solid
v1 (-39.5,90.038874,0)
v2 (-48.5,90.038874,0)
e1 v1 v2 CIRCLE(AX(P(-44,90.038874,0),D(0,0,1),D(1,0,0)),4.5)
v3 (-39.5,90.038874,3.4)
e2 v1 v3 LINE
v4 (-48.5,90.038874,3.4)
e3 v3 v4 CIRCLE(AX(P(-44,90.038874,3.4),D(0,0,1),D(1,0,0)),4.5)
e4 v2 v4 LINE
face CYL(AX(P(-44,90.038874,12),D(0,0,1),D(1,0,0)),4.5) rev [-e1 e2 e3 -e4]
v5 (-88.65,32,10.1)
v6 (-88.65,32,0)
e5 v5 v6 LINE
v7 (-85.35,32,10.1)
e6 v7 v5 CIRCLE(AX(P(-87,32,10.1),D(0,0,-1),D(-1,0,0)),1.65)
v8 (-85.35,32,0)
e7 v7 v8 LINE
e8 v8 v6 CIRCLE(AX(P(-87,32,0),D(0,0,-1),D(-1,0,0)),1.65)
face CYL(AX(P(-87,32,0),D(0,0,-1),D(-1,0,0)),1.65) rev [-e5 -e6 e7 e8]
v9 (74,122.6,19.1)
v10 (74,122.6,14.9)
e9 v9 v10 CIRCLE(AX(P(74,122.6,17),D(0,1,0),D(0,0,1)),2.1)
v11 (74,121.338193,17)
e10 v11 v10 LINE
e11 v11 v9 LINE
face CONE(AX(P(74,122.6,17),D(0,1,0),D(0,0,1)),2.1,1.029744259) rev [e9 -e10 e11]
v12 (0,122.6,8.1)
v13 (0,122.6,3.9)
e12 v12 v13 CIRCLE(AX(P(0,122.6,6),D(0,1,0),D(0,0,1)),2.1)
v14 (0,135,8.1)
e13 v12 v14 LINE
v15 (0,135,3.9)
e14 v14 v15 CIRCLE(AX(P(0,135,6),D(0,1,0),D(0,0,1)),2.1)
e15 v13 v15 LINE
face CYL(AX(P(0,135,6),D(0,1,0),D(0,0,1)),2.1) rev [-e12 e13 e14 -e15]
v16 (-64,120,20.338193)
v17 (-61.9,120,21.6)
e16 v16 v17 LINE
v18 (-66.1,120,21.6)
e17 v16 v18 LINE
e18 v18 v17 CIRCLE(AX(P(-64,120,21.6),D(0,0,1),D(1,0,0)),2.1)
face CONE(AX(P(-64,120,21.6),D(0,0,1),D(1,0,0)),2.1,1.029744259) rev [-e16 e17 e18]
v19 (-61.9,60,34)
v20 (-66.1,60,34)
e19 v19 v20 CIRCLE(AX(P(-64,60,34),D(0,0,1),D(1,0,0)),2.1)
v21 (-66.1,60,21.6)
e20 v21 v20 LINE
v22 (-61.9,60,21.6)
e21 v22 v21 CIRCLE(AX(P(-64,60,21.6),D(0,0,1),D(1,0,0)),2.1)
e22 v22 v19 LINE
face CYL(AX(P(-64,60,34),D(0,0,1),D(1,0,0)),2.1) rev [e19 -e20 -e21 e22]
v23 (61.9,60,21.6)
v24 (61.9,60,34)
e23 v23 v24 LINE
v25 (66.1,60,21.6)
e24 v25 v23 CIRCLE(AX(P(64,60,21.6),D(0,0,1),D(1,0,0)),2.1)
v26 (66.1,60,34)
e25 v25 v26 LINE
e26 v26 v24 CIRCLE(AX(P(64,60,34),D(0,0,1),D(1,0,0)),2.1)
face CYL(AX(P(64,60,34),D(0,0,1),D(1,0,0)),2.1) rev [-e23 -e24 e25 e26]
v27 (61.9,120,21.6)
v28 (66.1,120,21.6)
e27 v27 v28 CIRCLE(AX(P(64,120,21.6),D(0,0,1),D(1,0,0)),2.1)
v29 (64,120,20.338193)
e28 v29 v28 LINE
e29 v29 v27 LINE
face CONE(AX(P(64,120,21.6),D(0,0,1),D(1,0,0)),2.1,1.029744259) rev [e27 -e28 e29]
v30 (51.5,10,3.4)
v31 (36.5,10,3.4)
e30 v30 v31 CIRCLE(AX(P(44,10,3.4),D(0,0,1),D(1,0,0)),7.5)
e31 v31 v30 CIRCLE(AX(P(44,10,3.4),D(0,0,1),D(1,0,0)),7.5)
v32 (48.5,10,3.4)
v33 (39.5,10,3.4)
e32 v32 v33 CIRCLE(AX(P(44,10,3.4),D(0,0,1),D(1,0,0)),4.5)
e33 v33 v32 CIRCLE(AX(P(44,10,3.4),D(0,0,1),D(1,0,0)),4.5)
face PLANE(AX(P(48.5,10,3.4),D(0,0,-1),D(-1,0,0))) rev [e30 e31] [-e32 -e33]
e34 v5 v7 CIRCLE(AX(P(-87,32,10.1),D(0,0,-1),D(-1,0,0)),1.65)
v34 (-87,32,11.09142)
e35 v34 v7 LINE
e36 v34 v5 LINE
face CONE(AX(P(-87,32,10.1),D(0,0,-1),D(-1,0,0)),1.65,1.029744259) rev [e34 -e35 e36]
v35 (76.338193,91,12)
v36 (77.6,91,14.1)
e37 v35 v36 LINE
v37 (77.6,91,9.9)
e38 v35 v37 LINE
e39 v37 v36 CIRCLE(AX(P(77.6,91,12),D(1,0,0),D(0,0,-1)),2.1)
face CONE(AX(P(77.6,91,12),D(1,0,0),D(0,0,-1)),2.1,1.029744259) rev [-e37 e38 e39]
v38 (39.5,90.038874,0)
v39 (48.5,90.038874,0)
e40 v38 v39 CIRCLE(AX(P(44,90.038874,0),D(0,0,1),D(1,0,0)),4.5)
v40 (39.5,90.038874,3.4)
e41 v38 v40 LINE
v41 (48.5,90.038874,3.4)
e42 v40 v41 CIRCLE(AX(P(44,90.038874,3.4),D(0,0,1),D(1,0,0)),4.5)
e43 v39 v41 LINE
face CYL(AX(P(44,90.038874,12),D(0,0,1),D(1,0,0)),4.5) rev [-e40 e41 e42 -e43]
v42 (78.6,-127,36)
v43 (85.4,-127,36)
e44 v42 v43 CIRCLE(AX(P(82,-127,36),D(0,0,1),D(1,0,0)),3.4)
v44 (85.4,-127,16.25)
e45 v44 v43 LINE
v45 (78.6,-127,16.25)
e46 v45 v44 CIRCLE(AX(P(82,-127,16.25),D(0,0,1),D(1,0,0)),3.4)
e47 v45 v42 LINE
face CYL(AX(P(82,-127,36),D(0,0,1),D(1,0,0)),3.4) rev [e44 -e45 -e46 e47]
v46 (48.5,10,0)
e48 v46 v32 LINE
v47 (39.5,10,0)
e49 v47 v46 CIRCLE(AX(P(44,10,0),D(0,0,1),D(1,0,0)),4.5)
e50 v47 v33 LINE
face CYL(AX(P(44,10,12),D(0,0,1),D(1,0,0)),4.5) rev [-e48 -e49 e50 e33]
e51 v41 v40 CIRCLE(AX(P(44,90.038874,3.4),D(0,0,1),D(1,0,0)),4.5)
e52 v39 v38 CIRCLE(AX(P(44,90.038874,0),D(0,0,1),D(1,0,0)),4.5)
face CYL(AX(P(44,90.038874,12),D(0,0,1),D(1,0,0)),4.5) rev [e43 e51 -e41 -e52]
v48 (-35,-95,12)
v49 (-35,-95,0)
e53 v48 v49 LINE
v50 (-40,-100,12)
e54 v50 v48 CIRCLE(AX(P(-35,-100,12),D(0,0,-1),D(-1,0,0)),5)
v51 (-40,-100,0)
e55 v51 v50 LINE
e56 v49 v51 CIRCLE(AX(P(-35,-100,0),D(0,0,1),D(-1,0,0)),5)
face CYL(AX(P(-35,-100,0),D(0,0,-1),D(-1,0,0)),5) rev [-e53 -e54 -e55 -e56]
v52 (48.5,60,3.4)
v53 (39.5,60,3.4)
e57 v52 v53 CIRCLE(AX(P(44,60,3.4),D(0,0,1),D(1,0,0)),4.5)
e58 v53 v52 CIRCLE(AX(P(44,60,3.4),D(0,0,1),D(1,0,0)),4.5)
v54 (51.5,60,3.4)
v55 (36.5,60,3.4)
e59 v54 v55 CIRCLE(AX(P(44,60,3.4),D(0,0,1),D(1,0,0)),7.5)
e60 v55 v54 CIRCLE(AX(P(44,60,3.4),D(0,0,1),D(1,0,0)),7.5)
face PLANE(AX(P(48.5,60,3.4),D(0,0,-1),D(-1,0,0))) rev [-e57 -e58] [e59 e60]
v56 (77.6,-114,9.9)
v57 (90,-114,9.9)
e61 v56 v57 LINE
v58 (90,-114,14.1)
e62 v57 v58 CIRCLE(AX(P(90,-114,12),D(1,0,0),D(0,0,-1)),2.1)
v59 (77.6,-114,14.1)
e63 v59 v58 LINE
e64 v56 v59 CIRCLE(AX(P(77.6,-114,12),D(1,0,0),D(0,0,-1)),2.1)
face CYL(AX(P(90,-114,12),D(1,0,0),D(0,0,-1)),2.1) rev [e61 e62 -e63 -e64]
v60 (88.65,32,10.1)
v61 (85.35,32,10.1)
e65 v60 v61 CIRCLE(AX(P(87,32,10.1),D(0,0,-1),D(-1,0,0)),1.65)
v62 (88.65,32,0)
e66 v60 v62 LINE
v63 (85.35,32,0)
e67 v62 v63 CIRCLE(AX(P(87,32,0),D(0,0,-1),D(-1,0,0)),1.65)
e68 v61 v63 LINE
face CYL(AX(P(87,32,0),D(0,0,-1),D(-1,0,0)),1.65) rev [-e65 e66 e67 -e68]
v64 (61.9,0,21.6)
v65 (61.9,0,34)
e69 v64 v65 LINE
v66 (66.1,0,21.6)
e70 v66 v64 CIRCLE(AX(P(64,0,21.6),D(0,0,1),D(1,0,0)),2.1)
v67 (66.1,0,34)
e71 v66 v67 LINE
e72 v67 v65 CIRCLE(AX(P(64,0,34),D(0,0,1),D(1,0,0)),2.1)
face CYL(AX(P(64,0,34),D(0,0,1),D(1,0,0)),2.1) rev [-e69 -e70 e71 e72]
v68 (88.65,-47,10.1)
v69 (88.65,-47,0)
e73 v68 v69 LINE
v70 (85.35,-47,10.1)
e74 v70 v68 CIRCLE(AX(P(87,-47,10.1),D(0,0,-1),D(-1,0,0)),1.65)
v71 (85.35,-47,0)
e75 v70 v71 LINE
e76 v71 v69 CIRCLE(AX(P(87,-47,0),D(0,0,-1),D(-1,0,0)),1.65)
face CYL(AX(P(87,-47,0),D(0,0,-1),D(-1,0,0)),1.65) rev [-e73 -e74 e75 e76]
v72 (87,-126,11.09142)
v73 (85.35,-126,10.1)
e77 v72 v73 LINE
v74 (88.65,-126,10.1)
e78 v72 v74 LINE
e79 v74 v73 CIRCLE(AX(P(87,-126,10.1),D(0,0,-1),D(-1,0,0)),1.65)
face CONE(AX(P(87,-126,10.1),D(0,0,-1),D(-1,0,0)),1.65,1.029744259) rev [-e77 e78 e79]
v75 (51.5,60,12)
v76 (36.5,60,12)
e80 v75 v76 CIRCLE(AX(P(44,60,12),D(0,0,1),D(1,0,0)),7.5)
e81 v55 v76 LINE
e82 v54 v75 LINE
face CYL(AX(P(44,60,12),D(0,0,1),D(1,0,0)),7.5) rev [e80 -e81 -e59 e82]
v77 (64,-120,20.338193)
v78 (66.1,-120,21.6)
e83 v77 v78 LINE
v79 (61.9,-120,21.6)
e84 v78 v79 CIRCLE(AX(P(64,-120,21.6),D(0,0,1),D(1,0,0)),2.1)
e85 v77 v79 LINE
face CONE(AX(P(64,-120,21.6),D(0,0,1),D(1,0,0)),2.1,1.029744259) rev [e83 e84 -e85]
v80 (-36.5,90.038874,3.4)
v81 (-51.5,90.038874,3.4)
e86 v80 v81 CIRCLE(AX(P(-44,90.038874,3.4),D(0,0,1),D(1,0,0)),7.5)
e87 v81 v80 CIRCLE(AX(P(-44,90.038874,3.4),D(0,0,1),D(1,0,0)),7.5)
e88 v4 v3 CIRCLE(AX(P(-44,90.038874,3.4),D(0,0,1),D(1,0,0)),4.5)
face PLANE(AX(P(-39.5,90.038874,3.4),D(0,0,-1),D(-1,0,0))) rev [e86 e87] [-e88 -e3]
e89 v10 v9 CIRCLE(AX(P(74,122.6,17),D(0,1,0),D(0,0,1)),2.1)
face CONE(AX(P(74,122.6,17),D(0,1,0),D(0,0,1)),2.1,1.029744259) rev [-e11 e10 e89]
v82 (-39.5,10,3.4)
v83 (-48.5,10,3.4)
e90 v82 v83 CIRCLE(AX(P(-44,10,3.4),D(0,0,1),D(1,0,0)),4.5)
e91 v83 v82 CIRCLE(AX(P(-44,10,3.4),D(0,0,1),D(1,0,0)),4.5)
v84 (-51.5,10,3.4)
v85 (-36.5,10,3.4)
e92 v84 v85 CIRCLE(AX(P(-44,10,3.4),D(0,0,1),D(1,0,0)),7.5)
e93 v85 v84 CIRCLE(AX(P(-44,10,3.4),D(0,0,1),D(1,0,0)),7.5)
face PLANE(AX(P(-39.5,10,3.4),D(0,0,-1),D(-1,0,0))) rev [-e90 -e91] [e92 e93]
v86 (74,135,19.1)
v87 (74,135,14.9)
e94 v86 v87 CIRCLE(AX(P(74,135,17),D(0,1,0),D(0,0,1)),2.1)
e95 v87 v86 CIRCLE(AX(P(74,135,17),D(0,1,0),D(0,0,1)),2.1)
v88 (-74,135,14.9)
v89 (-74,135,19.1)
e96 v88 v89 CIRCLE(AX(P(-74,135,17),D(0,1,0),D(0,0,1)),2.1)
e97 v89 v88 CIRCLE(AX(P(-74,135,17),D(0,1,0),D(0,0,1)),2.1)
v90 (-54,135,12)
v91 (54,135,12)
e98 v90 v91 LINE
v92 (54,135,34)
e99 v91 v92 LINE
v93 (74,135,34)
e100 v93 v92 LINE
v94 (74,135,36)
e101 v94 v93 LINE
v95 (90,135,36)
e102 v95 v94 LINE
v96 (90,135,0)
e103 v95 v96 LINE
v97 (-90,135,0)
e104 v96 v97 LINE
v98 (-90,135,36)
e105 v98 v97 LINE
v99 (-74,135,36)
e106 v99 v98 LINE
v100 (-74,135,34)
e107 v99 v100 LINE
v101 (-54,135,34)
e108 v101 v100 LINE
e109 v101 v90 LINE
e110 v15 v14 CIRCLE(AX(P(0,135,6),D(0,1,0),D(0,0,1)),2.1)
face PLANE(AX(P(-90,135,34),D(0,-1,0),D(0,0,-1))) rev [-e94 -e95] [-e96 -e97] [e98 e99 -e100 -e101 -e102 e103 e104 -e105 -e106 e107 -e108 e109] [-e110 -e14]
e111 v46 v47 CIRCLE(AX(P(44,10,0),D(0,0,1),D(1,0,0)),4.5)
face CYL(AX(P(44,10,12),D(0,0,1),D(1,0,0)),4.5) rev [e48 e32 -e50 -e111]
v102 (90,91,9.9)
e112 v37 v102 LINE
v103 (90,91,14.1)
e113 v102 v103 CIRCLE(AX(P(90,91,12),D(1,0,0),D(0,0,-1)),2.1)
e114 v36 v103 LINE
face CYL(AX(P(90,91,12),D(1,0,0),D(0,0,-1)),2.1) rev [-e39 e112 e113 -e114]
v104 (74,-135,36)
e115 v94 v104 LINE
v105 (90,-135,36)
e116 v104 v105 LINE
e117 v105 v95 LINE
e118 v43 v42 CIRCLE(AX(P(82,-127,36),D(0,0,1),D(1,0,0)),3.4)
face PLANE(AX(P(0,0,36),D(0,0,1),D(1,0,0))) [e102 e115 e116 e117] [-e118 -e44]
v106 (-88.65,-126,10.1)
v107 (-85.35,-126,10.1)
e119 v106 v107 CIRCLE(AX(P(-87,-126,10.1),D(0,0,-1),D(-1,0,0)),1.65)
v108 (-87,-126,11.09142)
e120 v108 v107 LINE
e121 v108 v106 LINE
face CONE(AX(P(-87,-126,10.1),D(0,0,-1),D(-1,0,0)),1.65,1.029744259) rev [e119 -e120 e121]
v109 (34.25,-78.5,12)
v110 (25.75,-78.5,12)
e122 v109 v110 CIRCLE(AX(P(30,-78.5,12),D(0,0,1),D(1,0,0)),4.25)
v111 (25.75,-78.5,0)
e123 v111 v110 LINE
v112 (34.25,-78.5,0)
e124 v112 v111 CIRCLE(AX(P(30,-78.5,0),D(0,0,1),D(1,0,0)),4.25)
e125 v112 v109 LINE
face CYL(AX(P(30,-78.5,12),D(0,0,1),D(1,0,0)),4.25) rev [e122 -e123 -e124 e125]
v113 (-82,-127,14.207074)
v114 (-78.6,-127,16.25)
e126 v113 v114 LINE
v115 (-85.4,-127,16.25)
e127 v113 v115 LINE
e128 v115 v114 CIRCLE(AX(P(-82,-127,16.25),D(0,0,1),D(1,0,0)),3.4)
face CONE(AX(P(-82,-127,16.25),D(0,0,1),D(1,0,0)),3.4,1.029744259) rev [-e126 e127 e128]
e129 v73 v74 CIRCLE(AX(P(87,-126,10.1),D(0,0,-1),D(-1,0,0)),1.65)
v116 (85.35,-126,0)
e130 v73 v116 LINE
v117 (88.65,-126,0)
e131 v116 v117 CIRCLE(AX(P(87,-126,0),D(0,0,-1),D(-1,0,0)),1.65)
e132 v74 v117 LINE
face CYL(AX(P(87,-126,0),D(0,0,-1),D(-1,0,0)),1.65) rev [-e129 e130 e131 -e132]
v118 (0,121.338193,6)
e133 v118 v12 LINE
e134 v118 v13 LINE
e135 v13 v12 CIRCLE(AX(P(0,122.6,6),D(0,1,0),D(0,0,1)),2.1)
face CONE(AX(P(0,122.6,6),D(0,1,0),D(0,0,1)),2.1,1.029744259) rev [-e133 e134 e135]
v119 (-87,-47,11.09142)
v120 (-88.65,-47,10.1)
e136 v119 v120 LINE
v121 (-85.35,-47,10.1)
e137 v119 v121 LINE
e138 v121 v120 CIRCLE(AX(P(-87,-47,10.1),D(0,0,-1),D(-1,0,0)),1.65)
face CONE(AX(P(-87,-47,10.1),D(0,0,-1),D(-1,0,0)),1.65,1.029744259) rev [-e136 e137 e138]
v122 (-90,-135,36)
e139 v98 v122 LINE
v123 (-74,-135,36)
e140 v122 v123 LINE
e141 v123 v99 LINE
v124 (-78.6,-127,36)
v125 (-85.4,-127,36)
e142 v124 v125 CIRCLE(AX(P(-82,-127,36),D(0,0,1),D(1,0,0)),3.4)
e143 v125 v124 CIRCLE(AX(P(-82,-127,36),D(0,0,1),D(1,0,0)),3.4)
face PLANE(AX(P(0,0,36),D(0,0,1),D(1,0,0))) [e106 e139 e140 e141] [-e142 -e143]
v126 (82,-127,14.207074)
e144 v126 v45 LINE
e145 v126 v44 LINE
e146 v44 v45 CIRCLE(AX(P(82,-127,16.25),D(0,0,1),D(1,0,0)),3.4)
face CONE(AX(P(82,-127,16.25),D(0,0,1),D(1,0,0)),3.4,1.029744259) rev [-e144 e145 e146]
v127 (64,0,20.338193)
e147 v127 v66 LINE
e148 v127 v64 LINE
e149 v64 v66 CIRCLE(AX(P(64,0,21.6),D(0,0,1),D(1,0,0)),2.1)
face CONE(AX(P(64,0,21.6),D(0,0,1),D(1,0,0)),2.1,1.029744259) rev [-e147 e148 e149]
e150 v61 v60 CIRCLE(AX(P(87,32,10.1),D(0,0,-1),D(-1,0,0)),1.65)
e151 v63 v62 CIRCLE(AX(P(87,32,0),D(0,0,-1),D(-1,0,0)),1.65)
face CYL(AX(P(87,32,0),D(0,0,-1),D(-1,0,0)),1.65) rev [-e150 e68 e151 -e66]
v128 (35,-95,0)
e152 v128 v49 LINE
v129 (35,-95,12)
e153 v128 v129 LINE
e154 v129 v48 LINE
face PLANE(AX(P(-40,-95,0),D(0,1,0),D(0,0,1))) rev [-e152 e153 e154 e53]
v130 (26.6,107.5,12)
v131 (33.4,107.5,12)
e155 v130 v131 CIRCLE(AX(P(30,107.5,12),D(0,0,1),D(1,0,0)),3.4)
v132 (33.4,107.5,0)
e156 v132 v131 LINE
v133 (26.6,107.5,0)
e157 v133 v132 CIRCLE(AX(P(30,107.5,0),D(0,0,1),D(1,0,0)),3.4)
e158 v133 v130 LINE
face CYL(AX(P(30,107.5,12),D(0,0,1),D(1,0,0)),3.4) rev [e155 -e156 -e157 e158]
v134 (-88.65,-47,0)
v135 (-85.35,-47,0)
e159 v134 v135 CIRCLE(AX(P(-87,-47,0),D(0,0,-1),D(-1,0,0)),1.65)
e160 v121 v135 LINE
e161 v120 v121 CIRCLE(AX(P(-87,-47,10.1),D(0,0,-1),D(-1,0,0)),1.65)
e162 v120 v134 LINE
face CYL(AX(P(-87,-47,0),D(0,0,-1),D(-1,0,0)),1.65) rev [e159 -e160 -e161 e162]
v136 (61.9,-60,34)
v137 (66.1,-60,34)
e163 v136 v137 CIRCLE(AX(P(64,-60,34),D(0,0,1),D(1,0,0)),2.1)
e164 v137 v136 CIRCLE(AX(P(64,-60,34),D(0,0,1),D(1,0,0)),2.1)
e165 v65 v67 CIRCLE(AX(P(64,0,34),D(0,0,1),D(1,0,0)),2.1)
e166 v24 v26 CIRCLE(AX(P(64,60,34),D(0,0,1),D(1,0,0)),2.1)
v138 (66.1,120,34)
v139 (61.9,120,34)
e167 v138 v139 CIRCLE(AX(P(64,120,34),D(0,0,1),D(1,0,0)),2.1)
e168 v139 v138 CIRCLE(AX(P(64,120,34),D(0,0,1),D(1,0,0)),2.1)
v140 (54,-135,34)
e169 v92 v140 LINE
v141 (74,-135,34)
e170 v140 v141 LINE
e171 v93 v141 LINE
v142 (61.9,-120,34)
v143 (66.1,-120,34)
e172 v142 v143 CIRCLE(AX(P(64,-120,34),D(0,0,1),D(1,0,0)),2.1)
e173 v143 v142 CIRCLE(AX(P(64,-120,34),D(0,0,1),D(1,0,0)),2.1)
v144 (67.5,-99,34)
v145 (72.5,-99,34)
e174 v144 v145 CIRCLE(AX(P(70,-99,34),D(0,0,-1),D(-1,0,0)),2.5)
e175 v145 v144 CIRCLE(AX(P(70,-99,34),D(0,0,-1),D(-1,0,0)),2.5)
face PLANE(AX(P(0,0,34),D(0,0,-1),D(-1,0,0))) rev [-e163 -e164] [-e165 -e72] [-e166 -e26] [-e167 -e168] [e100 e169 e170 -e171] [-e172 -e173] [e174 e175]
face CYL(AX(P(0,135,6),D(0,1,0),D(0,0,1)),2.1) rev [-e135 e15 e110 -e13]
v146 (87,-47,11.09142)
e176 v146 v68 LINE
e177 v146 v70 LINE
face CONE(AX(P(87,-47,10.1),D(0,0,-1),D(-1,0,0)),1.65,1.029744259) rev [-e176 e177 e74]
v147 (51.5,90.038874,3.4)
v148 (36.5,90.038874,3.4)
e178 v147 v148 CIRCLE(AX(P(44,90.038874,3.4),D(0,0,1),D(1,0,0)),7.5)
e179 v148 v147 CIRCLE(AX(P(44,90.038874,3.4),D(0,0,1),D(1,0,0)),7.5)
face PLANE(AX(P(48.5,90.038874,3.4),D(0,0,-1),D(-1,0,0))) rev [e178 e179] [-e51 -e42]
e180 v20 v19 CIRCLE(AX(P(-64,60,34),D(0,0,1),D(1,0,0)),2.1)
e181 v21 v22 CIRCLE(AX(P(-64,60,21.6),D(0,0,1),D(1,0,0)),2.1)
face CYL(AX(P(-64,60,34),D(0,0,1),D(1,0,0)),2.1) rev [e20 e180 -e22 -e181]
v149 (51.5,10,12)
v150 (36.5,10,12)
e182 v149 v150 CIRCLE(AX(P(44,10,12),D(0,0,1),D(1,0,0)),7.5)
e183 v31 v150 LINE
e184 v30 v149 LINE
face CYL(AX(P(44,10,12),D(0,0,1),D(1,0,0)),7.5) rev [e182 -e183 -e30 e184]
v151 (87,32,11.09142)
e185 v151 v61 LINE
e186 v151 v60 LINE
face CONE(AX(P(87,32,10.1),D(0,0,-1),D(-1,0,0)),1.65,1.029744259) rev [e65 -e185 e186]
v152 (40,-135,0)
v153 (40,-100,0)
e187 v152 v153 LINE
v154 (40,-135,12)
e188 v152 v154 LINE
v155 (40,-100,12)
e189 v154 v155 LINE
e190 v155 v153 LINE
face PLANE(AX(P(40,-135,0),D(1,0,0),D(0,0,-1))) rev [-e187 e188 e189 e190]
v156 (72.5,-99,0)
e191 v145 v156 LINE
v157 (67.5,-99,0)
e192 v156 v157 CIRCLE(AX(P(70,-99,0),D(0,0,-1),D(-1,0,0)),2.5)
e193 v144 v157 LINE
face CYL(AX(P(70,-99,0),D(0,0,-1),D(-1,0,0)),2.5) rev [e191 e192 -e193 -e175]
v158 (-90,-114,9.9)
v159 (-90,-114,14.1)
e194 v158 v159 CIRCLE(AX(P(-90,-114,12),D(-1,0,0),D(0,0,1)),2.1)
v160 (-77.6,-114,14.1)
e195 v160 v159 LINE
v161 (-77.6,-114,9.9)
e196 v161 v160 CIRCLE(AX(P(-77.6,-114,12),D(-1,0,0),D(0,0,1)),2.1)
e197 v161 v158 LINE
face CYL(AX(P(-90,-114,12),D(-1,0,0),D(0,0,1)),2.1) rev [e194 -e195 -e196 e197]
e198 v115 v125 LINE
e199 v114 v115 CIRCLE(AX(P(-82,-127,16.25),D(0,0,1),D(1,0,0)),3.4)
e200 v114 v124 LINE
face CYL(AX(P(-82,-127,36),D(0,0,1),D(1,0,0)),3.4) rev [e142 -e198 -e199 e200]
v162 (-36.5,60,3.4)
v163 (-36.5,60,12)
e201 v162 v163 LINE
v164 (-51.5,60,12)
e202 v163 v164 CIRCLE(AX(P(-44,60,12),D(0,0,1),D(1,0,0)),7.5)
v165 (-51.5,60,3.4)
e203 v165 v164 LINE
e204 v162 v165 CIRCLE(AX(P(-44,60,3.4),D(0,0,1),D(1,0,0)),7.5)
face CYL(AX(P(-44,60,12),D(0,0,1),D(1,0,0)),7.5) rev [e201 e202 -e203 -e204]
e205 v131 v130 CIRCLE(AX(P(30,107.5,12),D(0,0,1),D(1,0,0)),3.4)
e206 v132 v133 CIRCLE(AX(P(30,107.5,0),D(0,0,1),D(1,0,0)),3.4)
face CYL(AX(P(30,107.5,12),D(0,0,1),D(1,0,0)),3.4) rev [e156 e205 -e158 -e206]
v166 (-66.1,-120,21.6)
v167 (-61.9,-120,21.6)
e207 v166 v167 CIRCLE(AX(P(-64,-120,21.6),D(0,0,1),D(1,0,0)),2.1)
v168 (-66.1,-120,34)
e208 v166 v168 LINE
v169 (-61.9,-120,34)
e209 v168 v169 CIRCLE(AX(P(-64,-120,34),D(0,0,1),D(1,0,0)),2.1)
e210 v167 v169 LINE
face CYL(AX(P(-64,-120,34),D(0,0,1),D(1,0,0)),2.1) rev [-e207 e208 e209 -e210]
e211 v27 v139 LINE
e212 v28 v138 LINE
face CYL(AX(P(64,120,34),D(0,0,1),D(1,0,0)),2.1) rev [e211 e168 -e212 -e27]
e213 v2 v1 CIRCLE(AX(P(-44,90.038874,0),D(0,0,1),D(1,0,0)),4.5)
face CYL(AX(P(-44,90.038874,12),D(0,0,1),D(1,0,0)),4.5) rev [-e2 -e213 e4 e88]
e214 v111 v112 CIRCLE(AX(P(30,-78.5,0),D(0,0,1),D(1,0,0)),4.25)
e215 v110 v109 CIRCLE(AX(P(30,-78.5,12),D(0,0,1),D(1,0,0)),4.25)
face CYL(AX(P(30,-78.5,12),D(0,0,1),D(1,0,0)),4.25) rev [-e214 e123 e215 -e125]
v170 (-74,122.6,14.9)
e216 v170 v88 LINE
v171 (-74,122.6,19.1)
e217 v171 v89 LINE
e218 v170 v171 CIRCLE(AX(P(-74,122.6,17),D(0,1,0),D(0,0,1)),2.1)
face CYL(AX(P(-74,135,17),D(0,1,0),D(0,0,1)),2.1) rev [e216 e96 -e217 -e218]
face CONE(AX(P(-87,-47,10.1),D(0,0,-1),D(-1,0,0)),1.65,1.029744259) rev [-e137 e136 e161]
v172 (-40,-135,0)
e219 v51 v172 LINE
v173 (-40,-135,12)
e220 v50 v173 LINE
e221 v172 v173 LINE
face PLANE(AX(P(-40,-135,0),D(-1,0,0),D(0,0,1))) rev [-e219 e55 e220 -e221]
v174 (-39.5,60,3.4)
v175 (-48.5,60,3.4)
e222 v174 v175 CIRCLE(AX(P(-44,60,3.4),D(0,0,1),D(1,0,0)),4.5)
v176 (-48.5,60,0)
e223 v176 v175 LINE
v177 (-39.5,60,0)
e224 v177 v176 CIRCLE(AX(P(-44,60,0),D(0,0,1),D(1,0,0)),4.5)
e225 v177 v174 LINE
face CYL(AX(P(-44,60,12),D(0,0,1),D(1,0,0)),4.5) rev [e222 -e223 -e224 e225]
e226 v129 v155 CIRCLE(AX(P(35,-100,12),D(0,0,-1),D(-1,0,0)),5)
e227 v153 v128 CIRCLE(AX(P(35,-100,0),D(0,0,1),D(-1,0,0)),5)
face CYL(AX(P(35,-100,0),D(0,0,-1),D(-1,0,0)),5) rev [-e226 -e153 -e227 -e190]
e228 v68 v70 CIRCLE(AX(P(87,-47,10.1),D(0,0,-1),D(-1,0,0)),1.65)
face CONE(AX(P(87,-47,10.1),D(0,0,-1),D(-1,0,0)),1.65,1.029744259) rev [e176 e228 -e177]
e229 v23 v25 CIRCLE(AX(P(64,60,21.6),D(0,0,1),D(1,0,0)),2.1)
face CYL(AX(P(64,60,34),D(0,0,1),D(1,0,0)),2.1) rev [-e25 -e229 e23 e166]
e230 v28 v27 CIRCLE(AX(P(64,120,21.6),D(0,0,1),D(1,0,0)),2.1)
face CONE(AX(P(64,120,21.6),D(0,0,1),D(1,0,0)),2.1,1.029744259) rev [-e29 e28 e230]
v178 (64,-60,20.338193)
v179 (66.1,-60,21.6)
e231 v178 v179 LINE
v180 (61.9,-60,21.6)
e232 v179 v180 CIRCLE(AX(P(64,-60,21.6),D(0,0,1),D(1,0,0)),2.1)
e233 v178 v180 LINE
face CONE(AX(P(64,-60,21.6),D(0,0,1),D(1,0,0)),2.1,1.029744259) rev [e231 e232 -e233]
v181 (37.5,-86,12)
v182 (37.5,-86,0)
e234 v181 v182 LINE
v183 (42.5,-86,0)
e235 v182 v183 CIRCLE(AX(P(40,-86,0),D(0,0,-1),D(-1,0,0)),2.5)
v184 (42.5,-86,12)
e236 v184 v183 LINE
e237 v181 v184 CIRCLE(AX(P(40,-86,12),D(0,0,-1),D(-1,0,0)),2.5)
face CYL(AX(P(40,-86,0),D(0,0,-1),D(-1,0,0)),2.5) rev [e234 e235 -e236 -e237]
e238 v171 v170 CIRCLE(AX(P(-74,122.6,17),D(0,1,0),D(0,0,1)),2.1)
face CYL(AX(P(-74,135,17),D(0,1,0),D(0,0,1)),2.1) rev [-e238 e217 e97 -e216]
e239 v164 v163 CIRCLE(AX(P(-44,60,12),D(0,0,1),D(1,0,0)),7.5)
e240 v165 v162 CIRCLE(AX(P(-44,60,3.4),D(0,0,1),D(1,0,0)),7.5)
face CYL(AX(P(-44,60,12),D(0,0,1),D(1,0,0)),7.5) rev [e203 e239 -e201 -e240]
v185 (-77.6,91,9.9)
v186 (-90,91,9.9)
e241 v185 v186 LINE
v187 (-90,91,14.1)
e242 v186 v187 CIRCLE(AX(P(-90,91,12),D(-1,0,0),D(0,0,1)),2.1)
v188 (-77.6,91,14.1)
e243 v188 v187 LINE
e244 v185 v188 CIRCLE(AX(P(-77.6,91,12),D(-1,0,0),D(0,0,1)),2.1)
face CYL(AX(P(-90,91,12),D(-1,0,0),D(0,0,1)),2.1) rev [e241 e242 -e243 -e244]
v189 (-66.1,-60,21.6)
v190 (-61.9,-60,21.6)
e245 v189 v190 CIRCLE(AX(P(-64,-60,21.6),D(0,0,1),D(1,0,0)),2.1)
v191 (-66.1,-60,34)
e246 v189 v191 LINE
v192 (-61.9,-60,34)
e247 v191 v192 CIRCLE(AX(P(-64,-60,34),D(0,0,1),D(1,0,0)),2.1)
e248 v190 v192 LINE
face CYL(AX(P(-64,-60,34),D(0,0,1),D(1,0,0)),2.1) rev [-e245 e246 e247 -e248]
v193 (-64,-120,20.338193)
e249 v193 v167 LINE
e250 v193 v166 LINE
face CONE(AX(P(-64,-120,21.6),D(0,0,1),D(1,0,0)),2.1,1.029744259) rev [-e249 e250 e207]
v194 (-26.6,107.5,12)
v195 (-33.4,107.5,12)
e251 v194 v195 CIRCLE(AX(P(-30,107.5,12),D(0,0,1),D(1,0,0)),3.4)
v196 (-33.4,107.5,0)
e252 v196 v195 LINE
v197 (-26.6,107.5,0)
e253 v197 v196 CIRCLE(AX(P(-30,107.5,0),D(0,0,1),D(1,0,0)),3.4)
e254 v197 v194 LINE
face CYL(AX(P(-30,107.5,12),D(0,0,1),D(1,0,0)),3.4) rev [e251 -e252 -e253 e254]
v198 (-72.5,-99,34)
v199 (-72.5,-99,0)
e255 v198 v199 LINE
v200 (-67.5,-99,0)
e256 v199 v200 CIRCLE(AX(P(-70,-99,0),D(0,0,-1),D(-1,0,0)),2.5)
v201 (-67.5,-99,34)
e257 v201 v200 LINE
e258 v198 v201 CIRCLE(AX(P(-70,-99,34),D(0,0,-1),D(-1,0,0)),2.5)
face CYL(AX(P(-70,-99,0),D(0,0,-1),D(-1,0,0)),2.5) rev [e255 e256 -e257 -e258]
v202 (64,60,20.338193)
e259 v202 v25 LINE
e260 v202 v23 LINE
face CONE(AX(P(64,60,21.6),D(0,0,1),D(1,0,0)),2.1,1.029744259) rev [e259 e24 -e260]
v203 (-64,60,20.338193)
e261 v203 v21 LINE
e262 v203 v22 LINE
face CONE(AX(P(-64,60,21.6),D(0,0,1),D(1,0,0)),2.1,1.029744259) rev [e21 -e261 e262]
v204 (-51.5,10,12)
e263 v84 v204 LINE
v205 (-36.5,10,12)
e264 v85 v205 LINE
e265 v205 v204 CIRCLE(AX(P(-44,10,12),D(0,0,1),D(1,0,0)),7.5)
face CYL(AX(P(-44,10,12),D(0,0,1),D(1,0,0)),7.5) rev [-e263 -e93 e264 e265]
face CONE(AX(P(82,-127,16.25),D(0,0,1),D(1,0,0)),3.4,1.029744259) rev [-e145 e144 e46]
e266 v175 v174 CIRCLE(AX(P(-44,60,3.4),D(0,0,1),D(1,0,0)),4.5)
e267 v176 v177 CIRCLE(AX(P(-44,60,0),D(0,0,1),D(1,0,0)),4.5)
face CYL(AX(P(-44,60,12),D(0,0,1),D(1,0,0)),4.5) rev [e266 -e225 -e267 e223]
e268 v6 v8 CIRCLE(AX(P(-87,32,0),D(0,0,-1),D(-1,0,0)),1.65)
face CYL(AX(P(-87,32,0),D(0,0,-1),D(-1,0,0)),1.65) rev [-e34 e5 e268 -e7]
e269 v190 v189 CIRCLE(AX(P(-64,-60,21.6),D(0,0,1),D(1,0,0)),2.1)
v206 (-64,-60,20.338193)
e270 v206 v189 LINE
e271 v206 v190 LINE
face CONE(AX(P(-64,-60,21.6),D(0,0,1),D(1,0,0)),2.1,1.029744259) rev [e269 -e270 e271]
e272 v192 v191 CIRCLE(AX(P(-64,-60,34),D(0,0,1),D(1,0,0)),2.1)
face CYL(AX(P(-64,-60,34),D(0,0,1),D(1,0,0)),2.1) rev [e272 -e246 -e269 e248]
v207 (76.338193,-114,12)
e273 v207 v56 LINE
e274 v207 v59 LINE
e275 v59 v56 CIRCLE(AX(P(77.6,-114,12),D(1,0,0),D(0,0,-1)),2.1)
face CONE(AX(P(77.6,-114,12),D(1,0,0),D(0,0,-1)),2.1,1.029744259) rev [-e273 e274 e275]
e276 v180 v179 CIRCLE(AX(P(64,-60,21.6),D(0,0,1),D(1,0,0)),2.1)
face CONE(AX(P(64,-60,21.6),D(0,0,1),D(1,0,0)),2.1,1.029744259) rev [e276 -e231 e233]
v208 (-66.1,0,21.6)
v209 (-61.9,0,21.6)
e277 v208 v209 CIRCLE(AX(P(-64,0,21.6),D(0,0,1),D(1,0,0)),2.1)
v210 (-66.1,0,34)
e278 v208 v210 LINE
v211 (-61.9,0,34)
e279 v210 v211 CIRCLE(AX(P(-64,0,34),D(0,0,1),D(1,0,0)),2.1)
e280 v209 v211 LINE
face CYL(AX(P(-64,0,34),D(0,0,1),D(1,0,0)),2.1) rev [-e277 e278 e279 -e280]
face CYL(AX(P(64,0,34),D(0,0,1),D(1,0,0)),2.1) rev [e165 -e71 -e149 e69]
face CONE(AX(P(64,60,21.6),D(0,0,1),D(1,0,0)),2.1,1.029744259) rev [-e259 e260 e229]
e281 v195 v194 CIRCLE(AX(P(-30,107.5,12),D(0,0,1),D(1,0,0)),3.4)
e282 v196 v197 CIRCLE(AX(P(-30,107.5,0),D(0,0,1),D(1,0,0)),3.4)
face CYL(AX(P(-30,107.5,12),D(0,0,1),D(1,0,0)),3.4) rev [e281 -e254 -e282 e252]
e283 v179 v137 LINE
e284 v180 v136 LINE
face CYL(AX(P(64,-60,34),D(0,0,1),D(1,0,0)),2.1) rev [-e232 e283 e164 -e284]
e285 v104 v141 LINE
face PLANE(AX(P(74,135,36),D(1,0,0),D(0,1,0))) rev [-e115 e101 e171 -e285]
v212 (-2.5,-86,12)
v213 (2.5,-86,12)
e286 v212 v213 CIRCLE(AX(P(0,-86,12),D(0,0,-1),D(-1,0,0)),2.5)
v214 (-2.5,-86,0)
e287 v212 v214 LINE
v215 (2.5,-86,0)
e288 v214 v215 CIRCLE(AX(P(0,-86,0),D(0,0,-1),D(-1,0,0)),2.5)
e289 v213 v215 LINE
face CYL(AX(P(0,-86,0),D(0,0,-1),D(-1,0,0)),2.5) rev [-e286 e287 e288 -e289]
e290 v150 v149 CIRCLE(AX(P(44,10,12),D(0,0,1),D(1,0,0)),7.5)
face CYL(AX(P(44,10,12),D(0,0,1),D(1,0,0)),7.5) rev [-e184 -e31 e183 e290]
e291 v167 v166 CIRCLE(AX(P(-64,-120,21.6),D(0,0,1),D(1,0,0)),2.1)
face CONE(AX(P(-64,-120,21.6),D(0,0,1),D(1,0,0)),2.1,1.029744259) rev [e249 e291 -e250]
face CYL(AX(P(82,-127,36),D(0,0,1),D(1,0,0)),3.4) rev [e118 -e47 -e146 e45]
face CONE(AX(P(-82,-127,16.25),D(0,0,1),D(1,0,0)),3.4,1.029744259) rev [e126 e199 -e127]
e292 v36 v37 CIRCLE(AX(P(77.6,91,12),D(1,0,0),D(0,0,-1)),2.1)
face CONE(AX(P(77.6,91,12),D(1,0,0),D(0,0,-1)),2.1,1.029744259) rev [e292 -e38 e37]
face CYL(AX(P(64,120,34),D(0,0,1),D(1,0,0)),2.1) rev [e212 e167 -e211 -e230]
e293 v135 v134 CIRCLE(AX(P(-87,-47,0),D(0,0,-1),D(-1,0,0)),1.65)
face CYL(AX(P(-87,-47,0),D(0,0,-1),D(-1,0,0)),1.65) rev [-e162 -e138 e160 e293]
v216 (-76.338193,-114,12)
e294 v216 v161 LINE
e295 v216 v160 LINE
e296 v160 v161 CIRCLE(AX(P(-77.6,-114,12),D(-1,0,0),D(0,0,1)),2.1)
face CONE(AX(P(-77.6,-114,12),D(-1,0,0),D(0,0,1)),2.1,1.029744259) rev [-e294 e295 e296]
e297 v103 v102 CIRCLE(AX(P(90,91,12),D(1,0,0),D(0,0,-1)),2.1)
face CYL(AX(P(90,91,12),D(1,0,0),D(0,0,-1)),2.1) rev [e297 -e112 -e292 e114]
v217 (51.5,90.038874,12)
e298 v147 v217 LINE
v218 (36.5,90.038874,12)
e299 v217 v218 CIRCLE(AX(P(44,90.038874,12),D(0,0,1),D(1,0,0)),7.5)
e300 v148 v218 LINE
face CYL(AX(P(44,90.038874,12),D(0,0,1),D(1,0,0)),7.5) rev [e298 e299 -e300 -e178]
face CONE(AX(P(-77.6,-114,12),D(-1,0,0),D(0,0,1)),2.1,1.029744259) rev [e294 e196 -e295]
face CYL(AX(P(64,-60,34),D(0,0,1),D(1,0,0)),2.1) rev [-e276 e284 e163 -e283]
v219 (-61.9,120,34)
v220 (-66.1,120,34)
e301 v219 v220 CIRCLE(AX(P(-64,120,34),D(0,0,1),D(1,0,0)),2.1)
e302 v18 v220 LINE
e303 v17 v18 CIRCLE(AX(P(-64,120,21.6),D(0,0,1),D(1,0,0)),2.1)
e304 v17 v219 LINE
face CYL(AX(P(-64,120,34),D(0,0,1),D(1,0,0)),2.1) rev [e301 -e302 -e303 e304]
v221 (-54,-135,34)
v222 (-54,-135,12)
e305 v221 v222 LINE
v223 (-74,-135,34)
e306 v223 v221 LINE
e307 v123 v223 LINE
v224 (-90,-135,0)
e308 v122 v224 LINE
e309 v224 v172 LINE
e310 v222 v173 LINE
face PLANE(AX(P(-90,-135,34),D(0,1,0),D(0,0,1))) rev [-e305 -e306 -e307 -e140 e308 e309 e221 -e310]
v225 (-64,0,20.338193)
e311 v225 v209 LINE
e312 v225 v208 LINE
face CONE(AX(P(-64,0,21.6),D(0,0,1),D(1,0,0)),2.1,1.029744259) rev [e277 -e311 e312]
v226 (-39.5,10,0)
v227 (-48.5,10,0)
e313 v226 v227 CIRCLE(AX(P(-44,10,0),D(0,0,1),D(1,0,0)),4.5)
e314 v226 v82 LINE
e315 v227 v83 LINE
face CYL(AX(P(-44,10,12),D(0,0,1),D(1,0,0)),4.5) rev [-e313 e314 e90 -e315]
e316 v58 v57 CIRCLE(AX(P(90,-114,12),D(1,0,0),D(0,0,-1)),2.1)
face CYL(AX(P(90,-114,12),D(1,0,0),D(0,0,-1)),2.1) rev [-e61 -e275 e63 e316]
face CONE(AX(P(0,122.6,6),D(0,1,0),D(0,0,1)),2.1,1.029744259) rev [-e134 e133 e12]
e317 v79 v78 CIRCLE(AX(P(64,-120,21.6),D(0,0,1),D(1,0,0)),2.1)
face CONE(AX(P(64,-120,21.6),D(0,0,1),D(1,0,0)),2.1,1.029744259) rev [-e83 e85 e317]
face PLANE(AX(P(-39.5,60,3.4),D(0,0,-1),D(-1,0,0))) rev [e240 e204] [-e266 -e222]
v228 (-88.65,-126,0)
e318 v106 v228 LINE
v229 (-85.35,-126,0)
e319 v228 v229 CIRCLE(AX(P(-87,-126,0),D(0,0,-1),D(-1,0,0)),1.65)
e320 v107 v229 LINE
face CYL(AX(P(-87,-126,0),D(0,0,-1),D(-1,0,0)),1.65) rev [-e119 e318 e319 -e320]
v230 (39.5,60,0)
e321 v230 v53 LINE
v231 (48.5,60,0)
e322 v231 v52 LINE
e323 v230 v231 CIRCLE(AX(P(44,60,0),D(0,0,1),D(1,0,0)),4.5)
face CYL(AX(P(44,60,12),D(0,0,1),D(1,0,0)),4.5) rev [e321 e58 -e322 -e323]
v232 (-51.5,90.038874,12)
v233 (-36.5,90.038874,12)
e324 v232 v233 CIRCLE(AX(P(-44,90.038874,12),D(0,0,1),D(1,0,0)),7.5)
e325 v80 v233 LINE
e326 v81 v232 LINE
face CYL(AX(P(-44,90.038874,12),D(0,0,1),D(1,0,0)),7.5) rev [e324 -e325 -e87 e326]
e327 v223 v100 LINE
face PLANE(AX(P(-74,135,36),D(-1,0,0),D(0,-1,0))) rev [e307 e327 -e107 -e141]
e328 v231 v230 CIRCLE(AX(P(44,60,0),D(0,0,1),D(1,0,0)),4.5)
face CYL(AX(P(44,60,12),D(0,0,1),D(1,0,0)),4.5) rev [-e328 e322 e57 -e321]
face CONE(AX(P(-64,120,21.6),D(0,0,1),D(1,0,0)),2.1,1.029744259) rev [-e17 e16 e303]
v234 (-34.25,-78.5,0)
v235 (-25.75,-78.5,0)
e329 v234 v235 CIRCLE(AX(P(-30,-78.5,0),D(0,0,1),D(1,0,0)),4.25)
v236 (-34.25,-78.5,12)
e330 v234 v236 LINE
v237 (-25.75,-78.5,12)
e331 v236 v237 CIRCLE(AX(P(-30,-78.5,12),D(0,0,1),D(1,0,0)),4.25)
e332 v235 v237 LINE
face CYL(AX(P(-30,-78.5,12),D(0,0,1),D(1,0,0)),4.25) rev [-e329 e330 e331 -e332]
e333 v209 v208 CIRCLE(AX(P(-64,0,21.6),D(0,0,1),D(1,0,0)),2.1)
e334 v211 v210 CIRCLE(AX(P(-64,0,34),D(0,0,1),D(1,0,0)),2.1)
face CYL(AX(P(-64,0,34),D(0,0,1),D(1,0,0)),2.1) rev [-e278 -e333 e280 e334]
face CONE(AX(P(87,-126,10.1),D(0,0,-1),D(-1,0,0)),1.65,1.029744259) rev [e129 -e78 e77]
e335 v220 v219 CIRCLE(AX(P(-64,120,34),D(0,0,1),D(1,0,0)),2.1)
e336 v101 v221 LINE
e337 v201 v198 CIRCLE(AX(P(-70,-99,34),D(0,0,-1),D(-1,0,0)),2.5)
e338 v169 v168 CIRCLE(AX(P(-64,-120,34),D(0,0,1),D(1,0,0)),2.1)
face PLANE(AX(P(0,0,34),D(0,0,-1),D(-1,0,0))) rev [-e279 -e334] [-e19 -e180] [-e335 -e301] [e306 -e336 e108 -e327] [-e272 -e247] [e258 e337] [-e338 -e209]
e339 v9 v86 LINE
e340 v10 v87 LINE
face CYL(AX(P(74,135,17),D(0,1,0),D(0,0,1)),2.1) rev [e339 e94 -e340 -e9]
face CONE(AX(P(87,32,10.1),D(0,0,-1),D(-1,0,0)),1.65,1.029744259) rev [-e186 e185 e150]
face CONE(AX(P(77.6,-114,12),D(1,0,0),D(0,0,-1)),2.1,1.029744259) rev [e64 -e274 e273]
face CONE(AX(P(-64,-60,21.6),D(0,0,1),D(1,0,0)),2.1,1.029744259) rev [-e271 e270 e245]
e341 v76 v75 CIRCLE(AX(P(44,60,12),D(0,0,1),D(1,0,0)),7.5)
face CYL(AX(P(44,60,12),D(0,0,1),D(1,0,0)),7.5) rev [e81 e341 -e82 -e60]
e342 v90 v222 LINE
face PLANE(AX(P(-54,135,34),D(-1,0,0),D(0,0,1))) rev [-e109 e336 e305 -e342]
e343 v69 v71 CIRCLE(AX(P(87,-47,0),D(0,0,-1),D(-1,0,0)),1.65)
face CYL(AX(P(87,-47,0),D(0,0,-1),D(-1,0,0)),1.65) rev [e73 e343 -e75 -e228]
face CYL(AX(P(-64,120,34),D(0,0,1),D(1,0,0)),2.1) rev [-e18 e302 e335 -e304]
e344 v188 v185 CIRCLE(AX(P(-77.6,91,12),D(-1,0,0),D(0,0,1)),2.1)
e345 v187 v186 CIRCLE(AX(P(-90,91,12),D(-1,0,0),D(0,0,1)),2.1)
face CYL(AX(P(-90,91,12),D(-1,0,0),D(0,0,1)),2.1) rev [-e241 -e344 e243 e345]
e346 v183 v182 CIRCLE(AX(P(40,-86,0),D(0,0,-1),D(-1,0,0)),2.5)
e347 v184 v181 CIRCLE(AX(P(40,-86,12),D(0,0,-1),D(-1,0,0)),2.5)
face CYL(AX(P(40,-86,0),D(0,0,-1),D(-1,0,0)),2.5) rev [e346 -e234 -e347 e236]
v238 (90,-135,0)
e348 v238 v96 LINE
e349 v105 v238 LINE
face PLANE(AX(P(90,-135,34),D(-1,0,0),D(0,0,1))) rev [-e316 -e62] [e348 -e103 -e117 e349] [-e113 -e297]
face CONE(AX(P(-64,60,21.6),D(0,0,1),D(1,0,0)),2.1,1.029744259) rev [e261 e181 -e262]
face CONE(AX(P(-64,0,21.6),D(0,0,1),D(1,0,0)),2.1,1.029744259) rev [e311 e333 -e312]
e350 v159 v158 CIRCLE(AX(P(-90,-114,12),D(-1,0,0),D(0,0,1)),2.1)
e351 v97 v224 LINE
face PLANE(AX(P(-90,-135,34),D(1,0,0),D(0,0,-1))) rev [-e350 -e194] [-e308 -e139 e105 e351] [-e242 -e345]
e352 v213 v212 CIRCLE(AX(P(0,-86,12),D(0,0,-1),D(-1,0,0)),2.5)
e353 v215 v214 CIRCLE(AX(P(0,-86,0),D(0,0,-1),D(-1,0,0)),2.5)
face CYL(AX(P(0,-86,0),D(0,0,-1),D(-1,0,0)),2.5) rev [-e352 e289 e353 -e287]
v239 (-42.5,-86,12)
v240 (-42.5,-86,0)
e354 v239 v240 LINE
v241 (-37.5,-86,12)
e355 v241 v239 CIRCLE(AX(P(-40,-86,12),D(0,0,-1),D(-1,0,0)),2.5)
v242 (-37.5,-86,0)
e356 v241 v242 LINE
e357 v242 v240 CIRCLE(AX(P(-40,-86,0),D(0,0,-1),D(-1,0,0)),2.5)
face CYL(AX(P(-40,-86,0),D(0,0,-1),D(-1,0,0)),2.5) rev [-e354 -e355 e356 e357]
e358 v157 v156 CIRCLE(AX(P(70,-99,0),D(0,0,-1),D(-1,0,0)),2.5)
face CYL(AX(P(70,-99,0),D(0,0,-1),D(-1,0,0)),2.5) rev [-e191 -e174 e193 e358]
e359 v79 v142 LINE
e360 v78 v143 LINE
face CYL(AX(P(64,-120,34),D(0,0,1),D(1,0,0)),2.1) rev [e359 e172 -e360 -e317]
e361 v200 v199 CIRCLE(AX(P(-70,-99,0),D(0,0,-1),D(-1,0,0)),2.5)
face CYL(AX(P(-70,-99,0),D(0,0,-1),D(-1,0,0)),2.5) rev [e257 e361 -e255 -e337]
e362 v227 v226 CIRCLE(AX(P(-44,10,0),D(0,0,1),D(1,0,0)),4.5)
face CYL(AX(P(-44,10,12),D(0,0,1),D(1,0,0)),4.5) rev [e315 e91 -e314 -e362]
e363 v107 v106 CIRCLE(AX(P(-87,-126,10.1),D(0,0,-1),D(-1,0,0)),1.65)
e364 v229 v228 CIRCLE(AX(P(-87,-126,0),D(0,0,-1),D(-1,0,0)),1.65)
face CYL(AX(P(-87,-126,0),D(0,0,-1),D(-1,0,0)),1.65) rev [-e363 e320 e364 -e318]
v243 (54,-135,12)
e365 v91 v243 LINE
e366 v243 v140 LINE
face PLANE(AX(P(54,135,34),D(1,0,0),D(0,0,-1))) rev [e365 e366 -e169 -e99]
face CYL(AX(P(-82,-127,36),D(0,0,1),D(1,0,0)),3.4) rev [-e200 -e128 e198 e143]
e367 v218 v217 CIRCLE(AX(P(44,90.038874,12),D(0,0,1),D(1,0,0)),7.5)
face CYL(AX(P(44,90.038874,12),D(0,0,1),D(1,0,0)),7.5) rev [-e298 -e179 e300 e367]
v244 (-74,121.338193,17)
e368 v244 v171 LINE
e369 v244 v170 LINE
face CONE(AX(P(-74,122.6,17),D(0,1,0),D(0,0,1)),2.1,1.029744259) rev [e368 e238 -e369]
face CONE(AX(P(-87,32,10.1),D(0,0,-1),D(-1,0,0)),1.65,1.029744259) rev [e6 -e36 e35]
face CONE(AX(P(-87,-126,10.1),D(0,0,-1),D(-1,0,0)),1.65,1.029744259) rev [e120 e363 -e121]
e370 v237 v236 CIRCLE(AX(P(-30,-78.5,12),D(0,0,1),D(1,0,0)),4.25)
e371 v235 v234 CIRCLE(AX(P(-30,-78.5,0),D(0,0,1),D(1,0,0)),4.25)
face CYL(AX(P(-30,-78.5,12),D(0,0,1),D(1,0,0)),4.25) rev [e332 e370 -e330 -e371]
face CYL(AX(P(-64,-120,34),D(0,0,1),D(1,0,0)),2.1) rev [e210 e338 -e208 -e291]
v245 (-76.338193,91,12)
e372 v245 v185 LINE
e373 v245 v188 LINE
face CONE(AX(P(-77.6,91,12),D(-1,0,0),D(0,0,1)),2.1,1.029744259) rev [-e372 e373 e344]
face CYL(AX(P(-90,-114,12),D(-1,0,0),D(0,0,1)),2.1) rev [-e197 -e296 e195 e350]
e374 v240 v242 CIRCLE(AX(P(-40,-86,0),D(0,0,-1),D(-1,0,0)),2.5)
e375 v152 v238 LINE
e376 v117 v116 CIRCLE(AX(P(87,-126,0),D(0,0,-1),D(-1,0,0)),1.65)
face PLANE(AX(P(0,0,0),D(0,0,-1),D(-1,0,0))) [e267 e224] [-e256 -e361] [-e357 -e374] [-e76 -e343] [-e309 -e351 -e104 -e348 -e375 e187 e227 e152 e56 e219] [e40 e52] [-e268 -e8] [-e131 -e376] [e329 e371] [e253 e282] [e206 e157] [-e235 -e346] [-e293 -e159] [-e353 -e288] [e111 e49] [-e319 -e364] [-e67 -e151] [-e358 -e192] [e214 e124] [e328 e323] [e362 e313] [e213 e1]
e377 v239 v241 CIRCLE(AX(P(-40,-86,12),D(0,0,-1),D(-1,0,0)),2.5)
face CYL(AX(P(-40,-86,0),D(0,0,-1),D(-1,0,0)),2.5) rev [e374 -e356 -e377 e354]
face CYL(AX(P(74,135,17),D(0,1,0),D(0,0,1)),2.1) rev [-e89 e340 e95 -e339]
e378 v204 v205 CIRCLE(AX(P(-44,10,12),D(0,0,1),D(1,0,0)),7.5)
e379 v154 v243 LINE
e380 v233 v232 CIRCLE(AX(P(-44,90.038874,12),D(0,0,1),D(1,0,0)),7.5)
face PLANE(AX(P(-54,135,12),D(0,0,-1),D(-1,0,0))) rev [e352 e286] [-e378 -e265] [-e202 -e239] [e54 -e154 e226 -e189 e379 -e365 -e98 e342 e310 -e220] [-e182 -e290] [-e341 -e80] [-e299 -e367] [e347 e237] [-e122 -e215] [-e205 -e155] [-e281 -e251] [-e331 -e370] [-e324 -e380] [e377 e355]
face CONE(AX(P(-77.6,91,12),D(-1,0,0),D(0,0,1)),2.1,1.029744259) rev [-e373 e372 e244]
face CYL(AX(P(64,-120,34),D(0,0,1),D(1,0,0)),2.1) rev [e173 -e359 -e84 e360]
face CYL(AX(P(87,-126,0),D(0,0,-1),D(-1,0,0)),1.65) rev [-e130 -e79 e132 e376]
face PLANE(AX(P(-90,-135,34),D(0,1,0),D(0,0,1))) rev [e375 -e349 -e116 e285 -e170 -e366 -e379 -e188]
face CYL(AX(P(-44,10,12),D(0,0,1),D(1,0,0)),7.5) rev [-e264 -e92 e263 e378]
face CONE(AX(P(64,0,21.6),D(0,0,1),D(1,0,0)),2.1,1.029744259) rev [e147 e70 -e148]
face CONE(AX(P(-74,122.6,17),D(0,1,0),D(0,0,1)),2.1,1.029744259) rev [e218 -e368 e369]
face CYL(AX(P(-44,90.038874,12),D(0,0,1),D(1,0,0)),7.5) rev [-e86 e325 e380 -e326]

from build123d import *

# Parameters (mm, degrees)
SKETCH_1_W                     = 180
SKETCH_1_H                     = 270
EXTRUDE_1_DEPTH                = 34
SKETCH_2_W                     = 108
SKETCH_2_H                     = 22
CUT_EXTRUDE_1_DEPTH            = 287.628679654
SKETCH_3_W                     = 16
SKETCH_3_H                     = 270
EXTRUDE_2_DEPTH                = 2
HOLE_WIZARD_M8_1_D             = 6.8
HOLE_WIZARD_M8_1_DEPTH         = 19.75
HOLE_WIZARD_M8_1_TIP           = 2.042926105
SKETCH_6_W                     = 80
SKETCH_6_H                     = 40
CUT_EXTRUDE_2_DEPTH            = 165.015243194
FILLET_1_R                     = 5
HOLE_WIZARD_M5_1_D             = 4.2
HOLE_WIZARD_M5_1_DEPTH         = 12.4
HOLE_WIZARD_M5_1_TIP           = 1.2618073
HOLE_WIZARD_M6_1_D             = 5
HOLE_WIZARD_M6_1_DEPTH         = 15
HOLE_WIZARD_M6_1_TIP           = 1.502151548
HOLE_WIZARD_M8_2_D             = 6.8
HOLE_WIZARD_M10_1_D            = 8.5
HOLE_WIZARD_M8_1_2_D           = 9
HOLE_WIZARD_M8_1_2_CBORE_D     = 15
HOLE_WIZARD_M8_1_2_CBORE_DEPTH = 8.6
HOLE_WIZARD_M5_3_D             = 4.2
HOLE_WIZARD_M5_3_DEPTH         = 12.4
HOLE_WIZARD_M5_3_TIP           = 1.2618073
HOLE_WIZARD_M5_4_D             = 4.2
HOLE_WIZARD_M5_4_DEPTH         = 12.4
HOLE_WIZARD_M5_4_TIP           = 1.2618073
HOLE_WIZARD_M6_2_D             = 5
HOLE_WIZARD_M4_1_D             = 3.3
HOLE_WIZARD_M4_1_DEPTH         = 10.1
HOLE_WIZARD_M4_1_TIP           = 0.991420021
HOLE_WIZARD_M5_5_D             = 4.2
HOLE_WIZARD_M5_5_DEPTH         = 12.4
HOLE_WIZARD_M5_5_TIP           = 1.2618073


with BuildPart() as part:
    # 草图1 → 凸台-拉伸1 (new body)
    with BuildSketch(Plane.XY):
        Rectangle(SKETCH_1_W, SKETCH_1_H)
    extrude(amount=EXTRUDE_1_DEPTH)

    # 草图2 → 切除-拉伸1 (cut, through all)
    with BuildSketch(Plane.XZ.offset(135)):
        with Locations((0, 23)):
            Rectangle(SKETCH_2_W, SKETCH_2_H)
    extrude(amount=-CUT_EXTRUDE_1_DEPTH, mode=Mode.SUBTRACT)

    # 草图3 → 凸台-拉伸2 (add)
    with BuildSketch(Plane.XY.offset(34)):
        with Locations((-82, 0)):
            Rectangle(SKETCH_3_W, SKETCH_3_H)
        with Locations((82, 0)):
            Rectangle(SKETCH_3_W, SKETCH_3_H)
    extrude(amount=EXTRUDE_2_DEPTH)

    # Hole Wizard M8 _1
    with Locations(Plane.XY.offset(36)):
        with Locations((-82, -127), (82, -127)):
            Hole(HOLE_WIZARD_M8_1_D / 2, depth=HOLE_WIZARD_M8_1_DEPTH)
            with Locations((0, 0, -(HOLE_WIZARD_M8_1_DEPTH + HOLE_WIZARD_M8_1_TIP / 2))):  # 118° drill point
                Cone(0, HOLE_WIZARD_M8_1_D / 2, HOLE_WIZARD_M8_1_TIP, mode=Mode.SUBTRACT)

    # 草图6 → 切除-拉伸2 (cut, through all)
    with BuildSketch(Plane.XY.offset(12)):
        with Locations((0, -115)):
            Rectangle(SKETCH_6_W, SKETCH_6_H)
    extrude(amount=-CUT_EXTRUDE_2_DEPTH, mode=Mode.SUBTRACT)

    # 圆角1
    fillet_1_edges = [part.edges().sort_by_distance(p)[0] for p in [
        (40, -95, 6),
        (-40, -95, 6),
    ]]
    fillet(fillet_1_edges, radius=FILLET_1_R)

    # M5 螺纹孔1
    with Locations(Plane(origin=(0, 135, 0), x_dir=(1, 0, 0), z_dir=(0, 1, 0))):
        with Locations((-74, -17), (74, -17), (0, -6)):
            Hole(HOLE_WIZARD_M5_1_D / 2, depth=HOLE_WIZARD_M5_1_DEPTH)
            with Locations((0, 0, -(HOLE_WIZARD_M5_1_DEPTH + HOLE_WIZARD_M5_1_TIP / 2))):  # 118° drill point
                Cone(0, HOLE_WIZARD_M5_1_D / 2, HOLE_WIZARD_M5_1_TIP, mode=Mode.SUBTRACT)

    # M6 螺纹孔1
    with Locations(Plane(origin=(0, 0, 0), x_dir=(-1, 0, 0), z_dir=(0, 0, -1))):
        with Locations((-45.042166393, -86), (-5.042166393, -86), (34.957833607, -86)):
            Hole(HOLE_WIZARD_M6_1_D / 2, depth=HOLE_WIZARD_M6_1_DEPTH)
            with Locations((0, 0, -(HOLE_WIZARD_M6_1_DEPTH + HOLE_WIZARD_M6_1_TIP / 2))):  # 118° drill point
                Cone(0, HOLE_WIZARD_M6_1_D / 2, HOLE_WIZARD_M6_1_TIP, mode=Mode.SUBTRACT)

    # M8 螺纹孔2 (through all)
    with Locations(Plane.XY.offset(12)):
        with Locations((-30, 107.5), (30, 107.5)):
            Hole(HOLE_WIZARD_M8_2_D / 2)

    # M10 螺纹孔1 (through all)
    with Locations(Plane.XY.offset(12)):
        with Locations((-30, -78.5), (30, -78.5)):
            Hole(HOLE_WIZARD_M10_1_D / 2)

    # Hole Wizard M8 _1 2 (through all)
    with Locations(Plane.XY.offset(12)):
        with Locations((-44, 90.038874186), (-44, 10), (-44, 60), (44, 60), (44, 10), (44, 90.038874186)):
            CounterBoreHole(HOLE_WIZARD_M8_1_2_D / 2, HOLE_WIZARD_M8_1_2_CBORE_D / 2, HOLE_WIZARD_M8_1_2_CBORE_DEPTH)

    # M5 螺纹孔3
    with Locations(Plane.ZY.offset(90)):
        with Locations((12, 91), (12, -114)):
            Hole(HOLE_WIZARD_M5_3_D / 2, depth=HOLE_WIZARD_M5_3_DEPTH)
            with Locations((0, 0, -(HOLE_WIZARD_M5_3_DEPTH + HOLE_WIZARD_M5_3_TIP / 2))):  # 118° drill point
                Cone(0, HOLE_WIZARD_M5_3_D / 2, HOLE_WIZARD_M5_3_TIP, mode=Mode.SUBTRACT)

    # M5 螺纹孔4
    with Locations(Plane(origin=(90, 0, 0), x_dir=(0, 0, -1), z_dir=(1, 0, 0))):
        with Locations((-12, 91), (-12, -114)):
            Hole(HOLE_WIZARD_M5_4_D / 2, depth=HOLE_WIZARD_M5_4_DEPTH)
            with Locations((0, 0, -(HOLE_WIZARD_M5_4_DEPTH + HOLE_WIZARD_M5_4_TIP / 2))):  # 118° drill point
                Cone(0, HOLE_WIZARD_M5_4_D / 2, HOLE_WIZARD_M5_4_TIP, mode=Mode.SUBTRACT)

    # M6 螺纹孔2 (through all)
    with Locations(Plane(origin=(0, 0, 0), x_dir=(-1, 0, 0), z_dir=(0, 0, -1))):
        with Locations((-70, -99), (70, -99)):
            Hole(HOLE_WIZARD_M6_2_D / 2)

    # M4 螺纹孔1
    with Locations(Plane(origin=(0, 0, 0), x_dir=(-1, 0, 0), z_dir=(0, 0, -1))):
        with Locations((-87, 32), (-87, -47), (-87, -126), (87, -126), (87, -47), (87, 32)):
            Hole(HOLE_WIZARD_M4_1_D / 2, depth=HOLE_WIZARD_M4_1_DEPTH)
            with Locations((0, 0, -(HOLE_WIZARD_M4_1_DEPTH + HOLE_WIZARD_M4_1_TIP / 2))):  # 118° drill point
                Cone(0, HOLE_WIZARD_M4_1_D / 2, HOLE_WIZARD_M4_1_TIP, mode=Mode.SUBTRACT)

    # M5 螺纹孔5
    with Locations(Plane.XY.offset(34)):
        with Locations((-64, 0), (-64, 60), (-64, 120), (-64, -120), (-64, -60), (64, -60), (64, -120), (64, 120), (64, 60), (64, 0)):
            Hole(HOLE_WIZARD_M5_5_D / 2, depth=HOLE_WIZARD_M5_5_DEPTH)
            with Locations((0, 0, -(HOLE_WIZARD_M5_5_DEPTH + HOLE_WIZARD_M5_5_TIP / 2))):  # 118° drill point
                Cone(0, HOLE_WIZARD_M5_5_D / 2, HOLE_WIZARD_M5_5_TIP, mode=Mode.SUBTRACT)


solid = part.part
